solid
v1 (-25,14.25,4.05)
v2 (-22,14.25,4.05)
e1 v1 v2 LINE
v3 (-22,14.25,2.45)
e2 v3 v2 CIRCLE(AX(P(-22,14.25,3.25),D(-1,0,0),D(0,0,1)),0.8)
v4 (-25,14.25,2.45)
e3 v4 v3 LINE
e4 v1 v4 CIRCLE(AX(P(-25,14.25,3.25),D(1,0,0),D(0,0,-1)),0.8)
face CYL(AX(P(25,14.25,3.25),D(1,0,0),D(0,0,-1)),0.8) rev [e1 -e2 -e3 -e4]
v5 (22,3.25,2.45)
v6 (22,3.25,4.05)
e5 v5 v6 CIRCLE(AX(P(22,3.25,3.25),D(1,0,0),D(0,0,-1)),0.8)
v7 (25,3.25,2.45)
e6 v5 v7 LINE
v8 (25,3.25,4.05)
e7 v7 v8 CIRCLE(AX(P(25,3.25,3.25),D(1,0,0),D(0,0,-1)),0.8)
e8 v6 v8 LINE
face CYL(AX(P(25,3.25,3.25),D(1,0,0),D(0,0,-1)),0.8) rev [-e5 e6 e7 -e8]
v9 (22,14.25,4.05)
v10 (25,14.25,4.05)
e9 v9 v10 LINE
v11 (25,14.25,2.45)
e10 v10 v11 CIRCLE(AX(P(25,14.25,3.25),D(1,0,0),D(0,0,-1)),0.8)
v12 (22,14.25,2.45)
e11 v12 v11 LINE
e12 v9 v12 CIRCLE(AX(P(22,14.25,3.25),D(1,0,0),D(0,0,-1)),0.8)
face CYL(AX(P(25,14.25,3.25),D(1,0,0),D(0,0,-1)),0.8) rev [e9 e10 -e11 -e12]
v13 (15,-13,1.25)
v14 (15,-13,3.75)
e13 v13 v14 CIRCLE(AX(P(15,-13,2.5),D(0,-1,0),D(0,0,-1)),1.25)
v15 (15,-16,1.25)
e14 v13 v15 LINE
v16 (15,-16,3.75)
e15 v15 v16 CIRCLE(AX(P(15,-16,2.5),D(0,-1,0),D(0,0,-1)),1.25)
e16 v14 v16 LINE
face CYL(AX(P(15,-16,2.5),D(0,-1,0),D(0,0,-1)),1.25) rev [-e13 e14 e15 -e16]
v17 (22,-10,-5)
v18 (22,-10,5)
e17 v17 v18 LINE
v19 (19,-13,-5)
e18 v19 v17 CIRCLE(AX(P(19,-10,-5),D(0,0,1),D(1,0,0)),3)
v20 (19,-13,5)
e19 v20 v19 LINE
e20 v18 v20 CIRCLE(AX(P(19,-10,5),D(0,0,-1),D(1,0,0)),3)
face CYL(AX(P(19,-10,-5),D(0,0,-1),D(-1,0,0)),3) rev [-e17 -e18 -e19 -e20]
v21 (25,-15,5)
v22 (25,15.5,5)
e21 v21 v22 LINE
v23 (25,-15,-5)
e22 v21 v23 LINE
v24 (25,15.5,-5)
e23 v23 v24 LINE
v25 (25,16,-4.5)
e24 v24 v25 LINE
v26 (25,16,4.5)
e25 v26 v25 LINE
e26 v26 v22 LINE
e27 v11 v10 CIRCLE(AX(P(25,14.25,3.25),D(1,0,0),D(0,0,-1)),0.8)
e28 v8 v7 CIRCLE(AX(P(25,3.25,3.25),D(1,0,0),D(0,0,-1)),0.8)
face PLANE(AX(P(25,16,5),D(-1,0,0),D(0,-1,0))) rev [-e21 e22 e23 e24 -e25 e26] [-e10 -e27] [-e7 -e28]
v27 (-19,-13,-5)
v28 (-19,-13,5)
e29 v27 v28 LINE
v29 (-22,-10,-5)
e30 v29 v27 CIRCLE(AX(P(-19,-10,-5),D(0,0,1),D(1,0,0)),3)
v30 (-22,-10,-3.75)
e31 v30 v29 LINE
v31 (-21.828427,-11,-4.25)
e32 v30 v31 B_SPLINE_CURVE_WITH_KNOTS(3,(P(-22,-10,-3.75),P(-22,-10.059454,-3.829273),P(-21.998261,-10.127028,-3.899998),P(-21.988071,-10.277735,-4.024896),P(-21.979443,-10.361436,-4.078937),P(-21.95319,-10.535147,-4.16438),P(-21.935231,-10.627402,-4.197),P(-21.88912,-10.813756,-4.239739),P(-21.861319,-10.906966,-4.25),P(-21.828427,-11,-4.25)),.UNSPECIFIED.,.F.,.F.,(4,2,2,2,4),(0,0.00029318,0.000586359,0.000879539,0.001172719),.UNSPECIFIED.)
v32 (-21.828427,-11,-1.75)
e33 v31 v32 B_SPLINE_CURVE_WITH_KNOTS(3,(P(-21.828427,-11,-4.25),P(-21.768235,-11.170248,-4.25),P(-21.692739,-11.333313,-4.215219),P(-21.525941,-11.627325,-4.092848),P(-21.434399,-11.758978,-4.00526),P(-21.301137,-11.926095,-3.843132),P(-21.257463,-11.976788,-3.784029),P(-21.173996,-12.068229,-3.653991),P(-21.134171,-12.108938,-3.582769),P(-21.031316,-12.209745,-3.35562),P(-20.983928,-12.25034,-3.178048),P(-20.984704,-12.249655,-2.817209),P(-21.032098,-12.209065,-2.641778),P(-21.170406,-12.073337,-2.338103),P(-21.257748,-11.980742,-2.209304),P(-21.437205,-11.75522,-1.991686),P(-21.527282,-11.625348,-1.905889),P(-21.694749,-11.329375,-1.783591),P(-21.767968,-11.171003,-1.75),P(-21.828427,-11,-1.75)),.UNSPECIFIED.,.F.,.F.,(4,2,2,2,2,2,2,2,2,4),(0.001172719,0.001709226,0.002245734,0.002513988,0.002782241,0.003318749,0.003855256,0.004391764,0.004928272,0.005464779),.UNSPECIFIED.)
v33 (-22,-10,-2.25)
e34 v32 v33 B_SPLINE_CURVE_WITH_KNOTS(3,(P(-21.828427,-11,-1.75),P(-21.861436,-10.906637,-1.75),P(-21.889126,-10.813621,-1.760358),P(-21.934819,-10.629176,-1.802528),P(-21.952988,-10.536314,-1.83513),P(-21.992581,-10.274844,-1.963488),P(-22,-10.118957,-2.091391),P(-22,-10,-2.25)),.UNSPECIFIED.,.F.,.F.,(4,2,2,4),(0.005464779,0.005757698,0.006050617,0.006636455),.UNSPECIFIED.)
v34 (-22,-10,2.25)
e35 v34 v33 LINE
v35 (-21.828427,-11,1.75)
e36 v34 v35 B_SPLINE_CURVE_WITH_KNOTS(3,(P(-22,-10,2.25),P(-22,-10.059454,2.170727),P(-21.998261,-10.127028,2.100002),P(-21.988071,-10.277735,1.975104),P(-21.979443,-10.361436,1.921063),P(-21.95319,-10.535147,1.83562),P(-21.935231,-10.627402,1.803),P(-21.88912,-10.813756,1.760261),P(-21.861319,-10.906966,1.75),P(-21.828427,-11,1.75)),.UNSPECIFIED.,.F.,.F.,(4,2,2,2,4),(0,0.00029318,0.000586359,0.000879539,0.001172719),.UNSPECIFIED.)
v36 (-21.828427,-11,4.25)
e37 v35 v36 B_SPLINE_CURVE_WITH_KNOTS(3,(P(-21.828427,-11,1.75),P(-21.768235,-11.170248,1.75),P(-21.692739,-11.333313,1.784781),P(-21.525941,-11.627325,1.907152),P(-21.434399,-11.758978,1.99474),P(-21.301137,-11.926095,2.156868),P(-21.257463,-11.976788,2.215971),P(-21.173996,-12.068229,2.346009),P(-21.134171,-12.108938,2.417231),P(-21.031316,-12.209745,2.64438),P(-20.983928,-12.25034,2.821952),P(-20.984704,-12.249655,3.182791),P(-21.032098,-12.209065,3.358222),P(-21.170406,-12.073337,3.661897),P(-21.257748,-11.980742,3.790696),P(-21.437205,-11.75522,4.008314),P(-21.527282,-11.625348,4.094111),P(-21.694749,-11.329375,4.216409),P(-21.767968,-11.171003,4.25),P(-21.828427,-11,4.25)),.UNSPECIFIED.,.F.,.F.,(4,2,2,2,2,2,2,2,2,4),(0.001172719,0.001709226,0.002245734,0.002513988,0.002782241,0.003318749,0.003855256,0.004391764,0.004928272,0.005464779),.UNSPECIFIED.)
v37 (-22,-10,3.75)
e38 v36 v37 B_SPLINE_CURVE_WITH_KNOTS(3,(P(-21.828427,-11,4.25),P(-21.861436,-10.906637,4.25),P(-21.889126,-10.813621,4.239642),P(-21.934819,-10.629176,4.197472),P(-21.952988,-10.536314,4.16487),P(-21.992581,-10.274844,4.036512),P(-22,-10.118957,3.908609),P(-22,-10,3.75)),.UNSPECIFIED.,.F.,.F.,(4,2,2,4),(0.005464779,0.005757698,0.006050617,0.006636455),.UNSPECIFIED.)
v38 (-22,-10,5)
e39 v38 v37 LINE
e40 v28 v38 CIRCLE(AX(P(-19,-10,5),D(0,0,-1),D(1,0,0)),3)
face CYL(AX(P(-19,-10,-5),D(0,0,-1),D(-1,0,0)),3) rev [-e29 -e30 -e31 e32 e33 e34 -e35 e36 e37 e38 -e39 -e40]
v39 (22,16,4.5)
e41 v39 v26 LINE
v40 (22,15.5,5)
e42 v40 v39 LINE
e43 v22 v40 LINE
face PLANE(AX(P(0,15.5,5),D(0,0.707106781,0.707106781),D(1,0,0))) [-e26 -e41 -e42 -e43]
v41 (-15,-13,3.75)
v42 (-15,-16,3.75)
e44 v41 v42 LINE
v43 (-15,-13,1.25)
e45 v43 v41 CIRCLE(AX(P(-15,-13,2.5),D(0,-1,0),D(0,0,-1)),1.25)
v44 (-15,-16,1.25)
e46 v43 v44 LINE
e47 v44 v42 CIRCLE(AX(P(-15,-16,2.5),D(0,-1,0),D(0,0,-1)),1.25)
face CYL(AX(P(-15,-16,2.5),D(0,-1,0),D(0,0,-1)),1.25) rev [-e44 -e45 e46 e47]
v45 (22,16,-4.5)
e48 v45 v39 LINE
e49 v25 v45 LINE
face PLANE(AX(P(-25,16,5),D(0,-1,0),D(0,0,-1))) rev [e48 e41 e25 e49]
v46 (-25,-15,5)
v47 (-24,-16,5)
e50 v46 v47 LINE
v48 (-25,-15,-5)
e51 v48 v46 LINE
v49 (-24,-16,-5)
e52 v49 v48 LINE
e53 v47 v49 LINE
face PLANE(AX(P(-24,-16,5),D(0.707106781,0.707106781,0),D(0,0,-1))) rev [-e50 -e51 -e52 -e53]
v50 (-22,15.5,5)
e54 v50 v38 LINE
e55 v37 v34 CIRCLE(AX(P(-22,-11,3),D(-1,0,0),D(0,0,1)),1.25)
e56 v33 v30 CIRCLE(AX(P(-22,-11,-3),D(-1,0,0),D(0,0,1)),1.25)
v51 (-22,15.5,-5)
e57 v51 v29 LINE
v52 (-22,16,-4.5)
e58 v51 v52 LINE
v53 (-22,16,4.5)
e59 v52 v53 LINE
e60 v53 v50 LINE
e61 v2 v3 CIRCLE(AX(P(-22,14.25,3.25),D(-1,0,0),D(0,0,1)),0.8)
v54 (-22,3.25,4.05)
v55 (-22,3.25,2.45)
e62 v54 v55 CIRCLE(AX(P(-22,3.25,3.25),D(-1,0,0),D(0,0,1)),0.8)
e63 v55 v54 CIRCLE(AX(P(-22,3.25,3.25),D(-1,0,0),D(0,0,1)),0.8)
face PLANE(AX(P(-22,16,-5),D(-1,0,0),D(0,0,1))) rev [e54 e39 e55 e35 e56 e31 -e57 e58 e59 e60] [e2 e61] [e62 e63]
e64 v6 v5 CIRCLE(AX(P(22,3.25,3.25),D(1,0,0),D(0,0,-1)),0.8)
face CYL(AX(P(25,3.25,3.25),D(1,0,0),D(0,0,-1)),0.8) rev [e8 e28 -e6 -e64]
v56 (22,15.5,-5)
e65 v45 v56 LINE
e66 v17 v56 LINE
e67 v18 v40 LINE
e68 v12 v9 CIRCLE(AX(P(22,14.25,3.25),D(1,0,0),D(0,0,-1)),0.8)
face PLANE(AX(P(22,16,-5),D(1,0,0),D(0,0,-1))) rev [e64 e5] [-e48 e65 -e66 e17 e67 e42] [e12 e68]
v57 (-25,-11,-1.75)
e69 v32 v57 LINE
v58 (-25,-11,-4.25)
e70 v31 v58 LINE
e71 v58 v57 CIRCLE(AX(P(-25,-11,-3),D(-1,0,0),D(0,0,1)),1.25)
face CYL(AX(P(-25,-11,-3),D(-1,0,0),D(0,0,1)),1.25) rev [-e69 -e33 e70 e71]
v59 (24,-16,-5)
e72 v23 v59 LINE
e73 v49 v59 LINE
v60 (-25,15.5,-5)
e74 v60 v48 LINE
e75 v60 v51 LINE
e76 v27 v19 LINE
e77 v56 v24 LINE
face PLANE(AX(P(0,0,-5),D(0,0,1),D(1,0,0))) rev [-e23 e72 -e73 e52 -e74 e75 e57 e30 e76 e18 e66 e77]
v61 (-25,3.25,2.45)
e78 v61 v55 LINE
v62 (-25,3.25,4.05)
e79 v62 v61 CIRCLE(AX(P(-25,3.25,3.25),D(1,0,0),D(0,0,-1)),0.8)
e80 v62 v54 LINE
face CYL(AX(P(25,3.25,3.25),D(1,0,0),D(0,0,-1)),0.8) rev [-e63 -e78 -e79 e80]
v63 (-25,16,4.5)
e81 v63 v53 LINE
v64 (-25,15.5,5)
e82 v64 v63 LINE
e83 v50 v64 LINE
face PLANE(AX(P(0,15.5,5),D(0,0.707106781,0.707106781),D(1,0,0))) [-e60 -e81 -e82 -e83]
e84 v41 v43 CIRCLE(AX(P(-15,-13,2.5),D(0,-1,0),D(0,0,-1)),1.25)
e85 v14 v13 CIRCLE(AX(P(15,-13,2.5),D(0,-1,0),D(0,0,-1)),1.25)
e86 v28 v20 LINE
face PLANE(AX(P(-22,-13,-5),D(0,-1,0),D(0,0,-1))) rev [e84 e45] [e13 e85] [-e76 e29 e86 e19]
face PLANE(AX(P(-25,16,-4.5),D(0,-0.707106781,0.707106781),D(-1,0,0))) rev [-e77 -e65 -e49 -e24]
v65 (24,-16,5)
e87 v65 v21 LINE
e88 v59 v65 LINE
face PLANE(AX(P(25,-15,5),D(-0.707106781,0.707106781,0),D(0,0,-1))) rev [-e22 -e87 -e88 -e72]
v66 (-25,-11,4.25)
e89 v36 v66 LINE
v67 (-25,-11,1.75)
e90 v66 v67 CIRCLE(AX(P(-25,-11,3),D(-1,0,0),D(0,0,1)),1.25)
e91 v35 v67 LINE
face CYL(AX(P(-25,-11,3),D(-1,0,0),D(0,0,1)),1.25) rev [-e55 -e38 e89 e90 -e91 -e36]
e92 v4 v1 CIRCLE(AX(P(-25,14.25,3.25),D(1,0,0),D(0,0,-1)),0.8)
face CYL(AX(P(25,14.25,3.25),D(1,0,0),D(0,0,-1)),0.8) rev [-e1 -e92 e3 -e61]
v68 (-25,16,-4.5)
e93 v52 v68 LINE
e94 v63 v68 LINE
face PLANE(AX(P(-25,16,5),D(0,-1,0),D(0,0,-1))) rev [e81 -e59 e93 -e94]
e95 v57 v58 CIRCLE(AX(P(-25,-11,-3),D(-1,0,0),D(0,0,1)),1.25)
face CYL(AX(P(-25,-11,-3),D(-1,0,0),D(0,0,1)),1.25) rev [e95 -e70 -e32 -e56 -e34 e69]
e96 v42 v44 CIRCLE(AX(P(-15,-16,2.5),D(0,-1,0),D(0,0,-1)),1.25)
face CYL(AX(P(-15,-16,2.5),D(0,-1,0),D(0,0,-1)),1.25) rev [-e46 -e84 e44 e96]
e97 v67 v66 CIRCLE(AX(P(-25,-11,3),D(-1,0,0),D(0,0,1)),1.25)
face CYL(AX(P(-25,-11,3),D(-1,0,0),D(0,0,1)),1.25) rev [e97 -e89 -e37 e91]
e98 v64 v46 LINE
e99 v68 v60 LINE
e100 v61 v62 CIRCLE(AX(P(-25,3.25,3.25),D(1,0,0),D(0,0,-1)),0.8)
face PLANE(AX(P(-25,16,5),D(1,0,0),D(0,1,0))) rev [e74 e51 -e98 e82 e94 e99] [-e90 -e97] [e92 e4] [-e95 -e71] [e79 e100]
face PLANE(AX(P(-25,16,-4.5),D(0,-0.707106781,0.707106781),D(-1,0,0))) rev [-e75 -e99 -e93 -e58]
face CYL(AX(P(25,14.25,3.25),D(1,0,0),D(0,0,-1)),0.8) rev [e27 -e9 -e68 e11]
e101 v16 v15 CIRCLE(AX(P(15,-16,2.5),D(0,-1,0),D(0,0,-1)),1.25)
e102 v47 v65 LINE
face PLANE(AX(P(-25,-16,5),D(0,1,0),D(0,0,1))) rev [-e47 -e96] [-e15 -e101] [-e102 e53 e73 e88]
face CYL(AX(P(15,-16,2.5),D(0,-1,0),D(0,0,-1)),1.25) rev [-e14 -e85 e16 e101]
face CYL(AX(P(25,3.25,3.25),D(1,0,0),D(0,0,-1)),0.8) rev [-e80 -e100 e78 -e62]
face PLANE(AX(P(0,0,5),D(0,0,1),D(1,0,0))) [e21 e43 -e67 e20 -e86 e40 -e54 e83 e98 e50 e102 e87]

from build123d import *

# Parameters (mm, degrees)
SKETCH26_W                 = 50
SKETCH26_H                 = 32
BOSS_EXTRUDE2_DEPTH        = 5
SKETCH27_W                 = 44
SKETCH27_H                 = 29
CUT_EXTRUDE5_DEPTH         = 32.320919527
FILLET1_R                  = 3
CHAMFER1_SIZE              = 0.5
CHAMFER2_SIZE              = 1
M2_TAPPED_HOLE1_D          = 1.6
F_2_5_2_5_DIAMETER_HOLE1_D = 2.5
M3_TAPPED_HOLE2_REACH      = 54.735
M3_TAPPED_HOLE2_BORE_R     = 1.25


with BuildPart() as part:
    # Sketch26 → Boss-Extrude2 (new, symmetric)
    with BuildSketch(Plane.XY):
        Rectangle(SKETCH26_W, SKETCH26_H)
    extrude(amount=BOSS_EXTRUDE2_DEPTH, both=True)

    # Sketch27 → Cut-Extrude5 (cut, through all)
    with BuildSketch(Plane.XY.offset(5)):
        with Locations((0, 1.5)):
            Rectangle(SKETCH27_W, SKETCH27_H)
    extrude(amount=-CUT_EXTRUDE5_DEPTH, mode=Mode.SUBTRACT)

    # Fillet1
    fillet1_edges = [part.edges().sort_by_distance(p)[0] for p in [
        (22, -13, 0),
        (-22, -13, 0),
    ]]
    fillet(fillet1_edges, radius=FILLET1_R)

    # Chamfer1
    chamfer1_edges = [part.edges().sort_by_distance(p)[0] for p in [
        (-23.5, 16, -5),
        (-23.5, 16, 5),
        (23.5, 16, -5),
        (23.5, 16, 5),
    ]]
    chamfer(chamfer1_edges, length=CHAMFER1_SIZE)

    # Chamfer2
    chamfer2_edges = [part.edges().sort_by_distance(p)[0] for p in [
        (25, -16, 0),
        (-25, -16, 0),
    ]]
    chamfer(chamfer2_edges, length=CHAMFER2_SIZE)

    # M2 Tapped Hole1 (through all)
    with Locations(Plane(origin=(25, 0, 0), x_dir=(0, 0, -1), z_dir=(1, 0, 0))):
        with Locations((-3.25, 14.25), (-3.25, 3.25)):
            Hole(M2_TAPPED_HOLE1_D / 2)

    # Ø2.5 (2.5) Diameter Hole1 (through all)
    with Locations(Plane(origin=(0, -16, 0), x_dir=(-1, 0, 0), z_dir=(0, -1, 0))):
        with Locations((15, -2.5), (-15, -2.5)):
            Hole(F_2_5_2_5_DIAMETER_HOLE1_D / 2)

    # M3 Tapped Hole2 bore → M3 Tapped Hole2 (cut, up to next)
    with BuildSketch(Plane.ZY.offset(25), mode=Mode.PRIVATE) as m3_tapped_hole2_sk1:
        with Locations((-3, -11)):
            Circle(M3_TAPPED_HOLE2_BORE_R)
    m3_tapped_hole2_tool1 = extrude(m3_tapped_hole2_sk1.sketch, amount=-M3_TAPPED_HOLE2_REACH, mode=Mode.PRIVATE) & part.part
    # M3 Tapped Hole2 bore → M3 Tapped Hole2 (cut, up to next)
    with BuildSketch(Plane.ZY.offset(25), mode=Mode.PRIVATE) as m3_tapped_hole2_sk2:
        with Locations((3, -11)):
            Circle(M3_TAPPED_HOLE2_BORE_R)
    m3_tapped_hole2_tool2 = extrude(m3_tapped_hole2_sk2.sketch, amount=-M3_TAPPED_HOLE2_REACH, mode=Mode.PRIVATE) & part.part
    add(m3_tapped_hole2_tool1.solids().sort_by_distance((-25, -11, -3))[0], mode=Mode.SUBTRACT)
    add(m3_tapped_hole2_tool2.solids().sort_by_distance((-25, -11, 3))[0], mode=Mode.SUBTRACT)


solid = part.part
